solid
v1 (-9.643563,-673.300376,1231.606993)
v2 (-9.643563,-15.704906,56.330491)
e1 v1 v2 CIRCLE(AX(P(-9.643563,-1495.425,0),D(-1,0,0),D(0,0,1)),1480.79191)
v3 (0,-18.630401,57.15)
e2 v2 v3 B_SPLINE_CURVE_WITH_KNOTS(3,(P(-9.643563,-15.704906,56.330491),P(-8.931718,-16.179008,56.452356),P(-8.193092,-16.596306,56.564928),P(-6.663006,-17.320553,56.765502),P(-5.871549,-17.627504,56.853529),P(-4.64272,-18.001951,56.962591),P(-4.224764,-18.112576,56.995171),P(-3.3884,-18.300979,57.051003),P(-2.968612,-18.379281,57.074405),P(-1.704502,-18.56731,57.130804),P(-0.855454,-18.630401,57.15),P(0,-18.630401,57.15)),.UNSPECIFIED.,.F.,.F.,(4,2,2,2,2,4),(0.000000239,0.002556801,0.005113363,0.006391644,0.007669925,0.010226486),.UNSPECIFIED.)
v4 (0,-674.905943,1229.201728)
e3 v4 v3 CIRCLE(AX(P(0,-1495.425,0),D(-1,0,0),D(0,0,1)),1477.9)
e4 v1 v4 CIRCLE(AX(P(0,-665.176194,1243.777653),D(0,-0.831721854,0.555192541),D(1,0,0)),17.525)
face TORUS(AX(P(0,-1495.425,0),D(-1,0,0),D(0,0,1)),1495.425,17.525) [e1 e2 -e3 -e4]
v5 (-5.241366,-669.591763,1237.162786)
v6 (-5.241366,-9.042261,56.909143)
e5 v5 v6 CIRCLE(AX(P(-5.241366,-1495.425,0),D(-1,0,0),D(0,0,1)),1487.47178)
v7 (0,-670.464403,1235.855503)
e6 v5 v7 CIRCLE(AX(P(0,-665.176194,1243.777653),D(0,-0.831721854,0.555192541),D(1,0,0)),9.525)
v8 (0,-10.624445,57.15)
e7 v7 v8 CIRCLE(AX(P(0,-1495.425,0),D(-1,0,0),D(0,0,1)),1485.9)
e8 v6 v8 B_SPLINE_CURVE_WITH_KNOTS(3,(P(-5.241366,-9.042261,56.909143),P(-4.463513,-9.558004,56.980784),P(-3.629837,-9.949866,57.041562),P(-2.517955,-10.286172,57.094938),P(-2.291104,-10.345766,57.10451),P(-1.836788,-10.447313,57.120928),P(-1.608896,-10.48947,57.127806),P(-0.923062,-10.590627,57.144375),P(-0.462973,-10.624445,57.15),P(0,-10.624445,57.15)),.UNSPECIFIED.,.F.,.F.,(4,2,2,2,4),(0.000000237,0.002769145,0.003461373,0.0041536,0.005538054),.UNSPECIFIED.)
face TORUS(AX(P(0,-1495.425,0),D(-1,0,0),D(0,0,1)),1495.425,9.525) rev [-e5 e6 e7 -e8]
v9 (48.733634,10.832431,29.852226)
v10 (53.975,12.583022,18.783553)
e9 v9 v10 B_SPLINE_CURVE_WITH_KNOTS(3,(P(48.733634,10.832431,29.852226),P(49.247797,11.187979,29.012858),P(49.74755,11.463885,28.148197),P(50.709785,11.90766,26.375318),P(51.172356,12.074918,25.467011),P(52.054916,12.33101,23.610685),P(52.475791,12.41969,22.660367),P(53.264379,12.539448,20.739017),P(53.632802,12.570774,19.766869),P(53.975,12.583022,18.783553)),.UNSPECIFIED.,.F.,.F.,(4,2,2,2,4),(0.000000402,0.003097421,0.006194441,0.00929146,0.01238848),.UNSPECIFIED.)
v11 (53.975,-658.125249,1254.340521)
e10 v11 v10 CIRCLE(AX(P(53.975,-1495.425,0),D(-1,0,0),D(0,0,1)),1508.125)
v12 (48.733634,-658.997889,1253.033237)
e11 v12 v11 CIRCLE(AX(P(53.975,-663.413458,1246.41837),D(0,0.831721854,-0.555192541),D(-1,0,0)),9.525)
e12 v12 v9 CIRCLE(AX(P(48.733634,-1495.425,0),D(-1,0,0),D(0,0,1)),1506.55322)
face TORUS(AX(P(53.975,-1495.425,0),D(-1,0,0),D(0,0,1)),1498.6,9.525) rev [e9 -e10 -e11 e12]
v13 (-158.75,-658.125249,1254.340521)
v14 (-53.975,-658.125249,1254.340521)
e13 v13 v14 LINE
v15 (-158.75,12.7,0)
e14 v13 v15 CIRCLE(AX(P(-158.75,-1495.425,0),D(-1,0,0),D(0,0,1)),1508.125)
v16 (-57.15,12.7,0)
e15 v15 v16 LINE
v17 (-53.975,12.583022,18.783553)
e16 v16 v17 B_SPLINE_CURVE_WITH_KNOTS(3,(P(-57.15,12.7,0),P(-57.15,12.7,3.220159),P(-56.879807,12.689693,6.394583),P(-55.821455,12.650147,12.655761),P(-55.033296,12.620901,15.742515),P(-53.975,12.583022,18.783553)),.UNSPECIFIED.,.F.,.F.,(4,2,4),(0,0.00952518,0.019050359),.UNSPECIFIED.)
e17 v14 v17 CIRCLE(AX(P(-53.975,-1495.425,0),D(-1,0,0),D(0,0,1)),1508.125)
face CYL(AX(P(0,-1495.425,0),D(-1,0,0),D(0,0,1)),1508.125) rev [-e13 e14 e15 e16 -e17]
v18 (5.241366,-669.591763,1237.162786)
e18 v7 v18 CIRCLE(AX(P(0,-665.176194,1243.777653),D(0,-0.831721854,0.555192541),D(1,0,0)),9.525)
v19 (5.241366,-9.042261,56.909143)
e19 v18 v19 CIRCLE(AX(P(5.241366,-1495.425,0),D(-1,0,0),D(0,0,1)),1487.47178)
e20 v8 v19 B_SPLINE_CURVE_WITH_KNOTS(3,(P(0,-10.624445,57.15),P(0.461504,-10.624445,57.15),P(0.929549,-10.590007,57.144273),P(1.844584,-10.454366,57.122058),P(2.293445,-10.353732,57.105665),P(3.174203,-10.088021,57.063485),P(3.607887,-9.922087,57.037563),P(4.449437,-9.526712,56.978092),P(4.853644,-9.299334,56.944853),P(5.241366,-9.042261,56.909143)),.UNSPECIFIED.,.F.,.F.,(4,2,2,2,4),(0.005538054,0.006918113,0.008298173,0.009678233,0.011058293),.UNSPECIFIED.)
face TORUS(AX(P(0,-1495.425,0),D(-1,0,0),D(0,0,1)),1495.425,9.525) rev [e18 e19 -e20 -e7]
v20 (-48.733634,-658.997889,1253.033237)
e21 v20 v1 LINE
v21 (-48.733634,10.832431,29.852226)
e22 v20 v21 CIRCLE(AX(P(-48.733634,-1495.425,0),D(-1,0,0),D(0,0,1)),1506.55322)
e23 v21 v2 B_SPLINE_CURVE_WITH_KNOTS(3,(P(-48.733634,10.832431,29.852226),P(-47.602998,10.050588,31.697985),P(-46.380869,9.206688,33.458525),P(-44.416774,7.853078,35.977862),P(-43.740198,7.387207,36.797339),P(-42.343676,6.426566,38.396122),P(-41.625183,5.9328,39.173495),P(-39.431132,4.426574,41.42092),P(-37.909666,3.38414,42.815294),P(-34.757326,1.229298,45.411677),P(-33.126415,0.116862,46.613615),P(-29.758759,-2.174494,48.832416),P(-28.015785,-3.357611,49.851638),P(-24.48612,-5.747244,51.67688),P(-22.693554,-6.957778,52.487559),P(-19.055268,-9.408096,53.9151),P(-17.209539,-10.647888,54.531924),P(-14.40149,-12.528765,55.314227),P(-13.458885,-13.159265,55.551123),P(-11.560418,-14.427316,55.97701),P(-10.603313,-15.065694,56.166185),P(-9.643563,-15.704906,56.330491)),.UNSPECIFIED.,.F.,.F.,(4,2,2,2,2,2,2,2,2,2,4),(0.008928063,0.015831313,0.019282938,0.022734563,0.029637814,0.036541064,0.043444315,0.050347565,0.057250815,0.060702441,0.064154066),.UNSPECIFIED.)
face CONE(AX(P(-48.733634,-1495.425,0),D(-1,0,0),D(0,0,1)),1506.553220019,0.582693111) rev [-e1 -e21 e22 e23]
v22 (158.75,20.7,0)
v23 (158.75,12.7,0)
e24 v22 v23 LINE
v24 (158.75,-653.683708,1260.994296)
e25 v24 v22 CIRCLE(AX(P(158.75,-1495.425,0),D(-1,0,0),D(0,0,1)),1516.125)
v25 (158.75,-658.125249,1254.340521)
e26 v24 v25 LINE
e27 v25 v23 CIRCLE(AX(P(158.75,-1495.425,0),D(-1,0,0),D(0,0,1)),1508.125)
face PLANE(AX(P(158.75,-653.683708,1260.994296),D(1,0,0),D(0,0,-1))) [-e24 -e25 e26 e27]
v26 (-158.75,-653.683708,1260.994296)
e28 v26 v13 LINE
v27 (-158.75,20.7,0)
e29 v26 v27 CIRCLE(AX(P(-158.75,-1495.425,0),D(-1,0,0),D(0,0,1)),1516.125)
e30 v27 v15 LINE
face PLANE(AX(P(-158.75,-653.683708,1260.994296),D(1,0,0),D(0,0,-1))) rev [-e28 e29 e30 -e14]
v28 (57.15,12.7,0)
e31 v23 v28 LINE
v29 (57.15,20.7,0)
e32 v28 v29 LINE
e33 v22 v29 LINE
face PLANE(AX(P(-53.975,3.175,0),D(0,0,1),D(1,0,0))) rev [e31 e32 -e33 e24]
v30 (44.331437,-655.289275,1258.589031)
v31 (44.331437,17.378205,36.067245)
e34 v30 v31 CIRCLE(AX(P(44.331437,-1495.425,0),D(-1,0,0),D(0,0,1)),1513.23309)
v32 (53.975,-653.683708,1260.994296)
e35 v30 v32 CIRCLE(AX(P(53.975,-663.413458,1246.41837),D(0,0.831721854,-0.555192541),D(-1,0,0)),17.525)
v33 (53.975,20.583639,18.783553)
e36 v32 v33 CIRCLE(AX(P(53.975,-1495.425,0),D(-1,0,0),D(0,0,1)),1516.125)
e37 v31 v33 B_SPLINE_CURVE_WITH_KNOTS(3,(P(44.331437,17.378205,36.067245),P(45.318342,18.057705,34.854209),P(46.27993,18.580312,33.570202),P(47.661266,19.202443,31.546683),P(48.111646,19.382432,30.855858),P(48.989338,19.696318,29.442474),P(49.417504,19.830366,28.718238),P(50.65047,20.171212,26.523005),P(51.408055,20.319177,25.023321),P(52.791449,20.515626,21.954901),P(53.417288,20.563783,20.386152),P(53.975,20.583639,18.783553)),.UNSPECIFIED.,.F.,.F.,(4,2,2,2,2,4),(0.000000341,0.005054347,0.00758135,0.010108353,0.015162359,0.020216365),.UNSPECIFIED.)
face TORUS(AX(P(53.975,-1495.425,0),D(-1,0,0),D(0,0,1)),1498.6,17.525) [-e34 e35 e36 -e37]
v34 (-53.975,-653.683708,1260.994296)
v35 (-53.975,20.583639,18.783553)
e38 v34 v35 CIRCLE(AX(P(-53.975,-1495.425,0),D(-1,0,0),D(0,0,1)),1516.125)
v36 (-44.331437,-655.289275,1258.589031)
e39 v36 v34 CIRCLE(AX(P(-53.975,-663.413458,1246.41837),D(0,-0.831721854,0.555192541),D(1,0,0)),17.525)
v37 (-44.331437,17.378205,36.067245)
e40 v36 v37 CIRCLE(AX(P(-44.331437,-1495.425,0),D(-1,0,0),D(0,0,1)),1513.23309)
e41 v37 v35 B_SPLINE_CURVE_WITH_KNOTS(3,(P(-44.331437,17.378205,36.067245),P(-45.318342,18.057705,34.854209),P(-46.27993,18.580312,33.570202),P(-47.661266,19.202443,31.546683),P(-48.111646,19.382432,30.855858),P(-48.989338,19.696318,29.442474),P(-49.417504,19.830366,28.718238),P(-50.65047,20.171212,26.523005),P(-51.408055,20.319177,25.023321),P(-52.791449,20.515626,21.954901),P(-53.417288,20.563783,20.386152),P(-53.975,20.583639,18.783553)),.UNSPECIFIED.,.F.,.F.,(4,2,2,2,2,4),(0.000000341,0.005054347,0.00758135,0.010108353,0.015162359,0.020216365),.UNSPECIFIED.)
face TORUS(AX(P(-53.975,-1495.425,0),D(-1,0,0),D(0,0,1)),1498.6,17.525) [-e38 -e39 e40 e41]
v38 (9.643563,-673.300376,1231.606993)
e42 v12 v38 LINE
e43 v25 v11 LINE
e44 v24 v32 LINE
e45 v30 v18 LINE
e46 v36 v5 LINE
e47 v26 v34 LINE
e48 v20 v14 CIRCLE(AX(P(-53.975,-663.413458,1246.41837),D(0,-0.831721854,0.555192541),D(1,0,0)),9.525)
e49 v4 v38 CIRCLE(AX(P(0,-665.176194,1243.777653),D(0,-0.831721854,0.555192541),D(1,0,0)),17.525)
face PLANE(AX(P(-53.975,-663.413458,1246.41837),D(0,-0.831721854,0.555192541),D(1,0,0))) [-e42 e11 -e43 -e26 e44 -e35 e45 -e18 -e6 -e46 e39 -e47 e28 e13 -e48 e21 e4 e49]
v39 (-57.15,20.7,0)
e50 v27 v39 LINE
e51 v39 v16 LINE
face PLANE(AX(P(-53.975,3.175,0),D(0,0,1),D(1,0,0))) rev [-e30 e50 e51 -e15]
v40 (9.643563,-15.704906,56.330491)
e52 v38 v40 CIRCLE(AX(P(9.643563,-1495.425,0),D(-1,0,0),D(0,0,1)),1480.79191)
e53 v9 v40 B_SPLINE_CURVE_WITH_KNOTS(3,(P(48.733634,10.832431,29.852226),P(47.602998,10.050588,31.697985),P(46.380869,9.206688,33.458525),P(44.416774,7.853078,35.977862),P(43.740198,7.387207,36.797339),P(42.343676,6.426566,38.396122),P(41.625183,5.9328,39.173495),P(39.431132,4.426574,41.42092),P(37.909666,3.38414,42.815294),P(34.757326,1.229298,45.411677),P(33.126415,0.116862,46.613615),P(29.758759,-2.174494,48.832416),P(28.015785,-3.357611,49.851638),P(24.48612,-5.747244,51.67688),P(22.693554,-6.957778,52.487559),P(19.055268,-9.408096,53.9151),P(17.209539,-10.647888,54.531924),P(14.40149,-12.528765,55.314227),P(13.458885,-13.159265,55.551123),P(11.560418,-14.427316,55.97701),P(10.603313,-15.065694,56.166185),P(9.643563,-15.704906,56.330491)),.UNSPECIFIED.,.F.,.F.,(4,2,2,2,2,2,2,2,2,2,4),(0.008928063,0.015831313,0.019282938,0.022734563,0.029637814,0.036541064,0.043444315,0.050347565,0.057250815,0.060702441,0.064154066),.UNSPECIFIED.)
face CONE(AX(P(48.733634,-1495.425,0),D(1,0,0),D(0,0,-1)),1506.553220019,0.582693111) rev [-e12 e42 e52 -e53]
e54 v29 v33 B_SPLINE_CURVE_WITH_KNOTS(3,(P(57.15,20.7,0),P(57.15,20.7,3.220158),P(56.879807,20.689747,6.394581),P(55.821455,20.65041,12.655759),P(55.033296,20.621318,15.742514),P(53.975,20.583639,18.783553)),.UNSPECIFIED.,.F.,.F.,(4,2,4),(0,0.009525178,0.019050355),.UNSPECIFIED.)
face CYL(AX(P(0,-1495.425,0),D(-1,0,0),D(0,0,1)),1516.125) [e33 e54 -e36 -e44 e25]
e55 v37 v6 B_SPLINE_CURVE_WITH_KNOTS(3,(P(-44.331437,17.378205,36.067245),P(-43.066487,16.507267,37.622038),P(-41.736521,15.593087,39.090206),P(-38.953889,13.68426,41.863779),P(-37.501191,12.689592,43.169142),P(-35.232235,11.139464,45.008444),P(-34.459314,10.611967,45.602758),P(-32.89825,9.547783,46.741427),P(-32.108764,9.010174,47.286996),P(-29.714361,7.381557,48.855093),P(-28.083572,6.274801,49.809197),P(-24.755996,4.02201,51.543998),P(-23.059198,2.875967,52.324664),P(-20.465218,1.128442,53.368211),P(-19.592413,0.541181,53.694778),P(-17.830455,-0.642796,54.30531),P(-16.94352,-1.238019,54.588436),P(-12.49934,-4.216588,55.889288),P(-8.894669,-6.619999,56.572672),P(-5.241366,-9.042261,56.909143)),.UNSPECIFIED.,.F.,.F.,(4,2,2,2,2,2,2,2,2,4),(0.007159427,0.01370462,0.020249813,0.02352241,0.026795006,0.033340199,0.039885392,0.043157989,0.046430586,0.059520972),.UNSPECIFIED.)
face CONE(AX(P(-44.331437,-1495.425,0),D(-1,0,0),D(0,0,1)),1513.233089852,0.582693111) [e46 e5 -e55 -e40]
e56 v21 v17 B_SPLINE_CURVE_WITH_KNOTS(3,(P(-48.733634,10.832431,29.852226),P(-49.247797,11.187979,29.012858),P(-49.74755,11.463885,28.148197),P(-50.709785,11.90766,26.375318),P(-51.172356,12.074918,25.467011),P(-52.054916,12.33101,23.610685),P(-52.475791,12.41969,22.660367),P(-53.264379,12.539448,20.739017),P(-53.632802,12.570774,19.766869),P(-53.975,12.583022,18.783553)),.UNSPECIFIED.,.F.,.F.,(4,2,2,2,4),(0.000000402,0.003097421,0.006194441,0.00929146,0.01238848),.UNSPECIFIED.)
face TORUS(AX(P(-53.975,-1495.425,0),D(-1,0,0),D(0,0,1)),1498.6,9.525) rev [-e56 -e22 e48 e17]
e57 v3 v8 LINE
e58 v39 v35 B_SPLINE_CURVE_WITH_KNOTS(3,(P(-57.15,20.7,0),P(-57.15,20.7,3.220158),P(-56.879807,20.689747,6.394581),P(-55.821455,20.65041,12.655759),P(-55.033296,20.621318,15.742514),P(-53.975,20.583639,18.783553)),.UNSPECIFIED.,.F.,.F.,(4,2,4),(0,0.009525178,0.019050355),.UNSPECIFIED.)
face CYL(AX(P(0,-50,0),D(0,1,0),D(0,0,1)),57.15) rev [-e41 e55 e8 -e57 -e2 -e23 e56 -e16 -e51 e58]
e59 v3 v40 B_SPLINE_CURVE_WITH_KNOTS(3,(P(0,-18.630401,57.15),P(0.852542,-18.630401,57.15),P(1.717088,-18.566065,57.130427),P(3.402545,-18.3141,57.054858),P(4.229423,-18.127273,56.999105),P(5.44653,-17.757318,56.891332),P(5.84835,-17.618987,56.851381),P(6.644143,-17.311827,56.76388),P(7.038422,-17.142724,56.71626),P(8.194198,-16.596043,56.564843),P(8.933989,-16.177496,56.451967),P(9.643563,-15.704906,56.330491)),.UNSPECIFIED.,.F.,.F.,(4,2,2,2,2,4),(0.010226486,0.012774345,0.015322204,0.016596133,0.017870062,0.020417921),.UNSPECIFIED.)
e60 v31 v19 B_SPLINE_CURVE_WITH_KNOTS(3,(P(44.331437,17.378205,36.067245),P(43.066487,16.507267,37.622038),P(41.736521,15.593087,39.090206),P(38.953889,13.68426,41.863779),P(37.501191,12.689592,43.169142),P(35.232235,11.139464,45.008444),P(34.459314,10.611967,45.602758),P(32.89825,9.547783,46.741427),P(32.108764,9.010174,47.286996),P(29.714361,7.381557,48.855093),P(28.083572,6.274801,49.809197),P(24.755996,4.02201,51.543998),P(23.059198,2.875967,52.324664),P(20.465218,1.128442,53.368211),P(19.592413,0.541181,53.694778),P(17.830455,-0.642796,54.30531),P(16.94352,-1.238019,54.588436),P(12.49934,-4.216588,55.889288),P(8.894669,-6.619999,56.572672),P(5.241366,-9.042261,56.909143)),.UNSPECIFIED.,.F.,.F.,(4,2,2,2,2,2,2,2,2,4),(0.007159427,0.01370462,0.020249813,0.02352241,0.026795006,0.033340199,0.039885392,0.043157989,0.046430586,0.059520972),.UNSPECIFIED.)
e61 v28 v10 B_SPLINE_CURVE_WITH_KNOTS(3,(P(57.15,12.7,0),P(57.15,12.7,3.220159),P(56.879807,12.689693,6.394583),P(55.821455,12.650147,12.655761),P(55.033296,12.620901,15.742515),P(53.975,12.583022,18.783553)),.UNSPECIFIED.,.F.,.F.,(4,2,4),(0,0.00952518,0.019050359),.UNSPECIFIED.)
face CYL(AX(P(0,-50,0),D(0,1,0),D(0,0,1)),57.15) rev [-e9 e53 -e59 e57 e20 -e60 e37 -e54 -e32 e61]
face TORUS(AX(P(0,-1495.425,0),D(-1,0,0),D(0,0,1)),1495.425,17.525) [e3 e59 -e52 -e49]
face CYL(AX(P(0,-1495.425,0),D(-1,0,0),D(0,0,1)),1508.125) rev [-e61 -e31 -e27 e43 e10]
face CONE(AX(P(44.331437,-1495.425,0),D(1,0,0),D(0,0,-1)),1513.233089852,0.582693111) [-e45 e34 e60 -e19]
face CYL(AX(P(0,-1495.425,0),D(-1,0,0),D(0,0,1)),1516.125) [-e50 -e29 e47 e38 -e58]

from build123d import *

# Parameters (mm, degrees)
SKETCH3_R          = 57.15
CUT_EXTRUDE1_DEPTH = 50


with BuildPart() as part:
    # Sweep1: sweep along a path in Sketch2
    with BuildLine(Plane(origin=(0, 0, 0), x_dir=(0, 0, -1), z_dir=(1, 0, 0))) as sweep1_path:
        ThreePointArc((0, 20.7), (-715, -158.48445696), (-1260.994295686, -653.683708467))
    # Sketch1 → Sweep1 (sweep)
    with BuildSketch(Plane.XY):
        with BuildLine():
            Line((-158.75, 20.7), (-53.975, 20.7))
            ThreePointArc((-53.975, 20.7), (-48.941078797, 19.961460685), (-44.331437049, 17.808089852))
            Line((-44.331437049, 17.808089852), (-5.241365883, -7.953220019))
            ThreePointArc((-5.241365883, -7.953220019), (0, -9.525), (5.241365883, -7.953220019))
            Line((5.241365883, -7.953220019), (44.331437049, 17.808089852))
            ThreePointArc((44.331437049, 17.808089852), (48.941078797, 19.961460685), (53.975, 20.7))
            Line((53.975, 20.7), (158.75, 20.7))
            Line((158.75, 20.7), (158.75, 12.7))
            Line((158.75, 12.7), (53.975, 12.7))
            ThreePointArc((53.975, 12.7), (51.23901715, 12.298597034), (48.733634117, 11.128220019))
            Line((48.733634117, 11.128220019), (9.643562951, -14.633089852))
            ThreePointArc((9.643562951, -14.633089852), (0, -17.525), (-9.643562951, -14.633089852))
            Line((-9.643562951, -14.633089852), (-48.733634117, 11.128220019))
            ThreePointArc((-48.733634117, 11.128220019), (-51.23901715, 12.298597034), (-53.975, 12.7))
            Line((-53.975, 12.7), (-158.75, 12.7))
            Line((-158.75, 12.7), (-158.75, 20.7))
        make_face()
    sweep(path=sweep1_path.line)

    # Sketch3 → Cut-Extrude1 (cut, symmetric)
    with BuildSketch(Plane(origin=(0, 0, 0), x_dir=(1, 0, 0), z_dir=(0, 1, 0))):
        Circle(SKETCH3_R)
    extrude(amount=CUT_EXTRUDE1_DEPTH, both=True, mode=Mode.SUBTRACT)


solid = part.part
